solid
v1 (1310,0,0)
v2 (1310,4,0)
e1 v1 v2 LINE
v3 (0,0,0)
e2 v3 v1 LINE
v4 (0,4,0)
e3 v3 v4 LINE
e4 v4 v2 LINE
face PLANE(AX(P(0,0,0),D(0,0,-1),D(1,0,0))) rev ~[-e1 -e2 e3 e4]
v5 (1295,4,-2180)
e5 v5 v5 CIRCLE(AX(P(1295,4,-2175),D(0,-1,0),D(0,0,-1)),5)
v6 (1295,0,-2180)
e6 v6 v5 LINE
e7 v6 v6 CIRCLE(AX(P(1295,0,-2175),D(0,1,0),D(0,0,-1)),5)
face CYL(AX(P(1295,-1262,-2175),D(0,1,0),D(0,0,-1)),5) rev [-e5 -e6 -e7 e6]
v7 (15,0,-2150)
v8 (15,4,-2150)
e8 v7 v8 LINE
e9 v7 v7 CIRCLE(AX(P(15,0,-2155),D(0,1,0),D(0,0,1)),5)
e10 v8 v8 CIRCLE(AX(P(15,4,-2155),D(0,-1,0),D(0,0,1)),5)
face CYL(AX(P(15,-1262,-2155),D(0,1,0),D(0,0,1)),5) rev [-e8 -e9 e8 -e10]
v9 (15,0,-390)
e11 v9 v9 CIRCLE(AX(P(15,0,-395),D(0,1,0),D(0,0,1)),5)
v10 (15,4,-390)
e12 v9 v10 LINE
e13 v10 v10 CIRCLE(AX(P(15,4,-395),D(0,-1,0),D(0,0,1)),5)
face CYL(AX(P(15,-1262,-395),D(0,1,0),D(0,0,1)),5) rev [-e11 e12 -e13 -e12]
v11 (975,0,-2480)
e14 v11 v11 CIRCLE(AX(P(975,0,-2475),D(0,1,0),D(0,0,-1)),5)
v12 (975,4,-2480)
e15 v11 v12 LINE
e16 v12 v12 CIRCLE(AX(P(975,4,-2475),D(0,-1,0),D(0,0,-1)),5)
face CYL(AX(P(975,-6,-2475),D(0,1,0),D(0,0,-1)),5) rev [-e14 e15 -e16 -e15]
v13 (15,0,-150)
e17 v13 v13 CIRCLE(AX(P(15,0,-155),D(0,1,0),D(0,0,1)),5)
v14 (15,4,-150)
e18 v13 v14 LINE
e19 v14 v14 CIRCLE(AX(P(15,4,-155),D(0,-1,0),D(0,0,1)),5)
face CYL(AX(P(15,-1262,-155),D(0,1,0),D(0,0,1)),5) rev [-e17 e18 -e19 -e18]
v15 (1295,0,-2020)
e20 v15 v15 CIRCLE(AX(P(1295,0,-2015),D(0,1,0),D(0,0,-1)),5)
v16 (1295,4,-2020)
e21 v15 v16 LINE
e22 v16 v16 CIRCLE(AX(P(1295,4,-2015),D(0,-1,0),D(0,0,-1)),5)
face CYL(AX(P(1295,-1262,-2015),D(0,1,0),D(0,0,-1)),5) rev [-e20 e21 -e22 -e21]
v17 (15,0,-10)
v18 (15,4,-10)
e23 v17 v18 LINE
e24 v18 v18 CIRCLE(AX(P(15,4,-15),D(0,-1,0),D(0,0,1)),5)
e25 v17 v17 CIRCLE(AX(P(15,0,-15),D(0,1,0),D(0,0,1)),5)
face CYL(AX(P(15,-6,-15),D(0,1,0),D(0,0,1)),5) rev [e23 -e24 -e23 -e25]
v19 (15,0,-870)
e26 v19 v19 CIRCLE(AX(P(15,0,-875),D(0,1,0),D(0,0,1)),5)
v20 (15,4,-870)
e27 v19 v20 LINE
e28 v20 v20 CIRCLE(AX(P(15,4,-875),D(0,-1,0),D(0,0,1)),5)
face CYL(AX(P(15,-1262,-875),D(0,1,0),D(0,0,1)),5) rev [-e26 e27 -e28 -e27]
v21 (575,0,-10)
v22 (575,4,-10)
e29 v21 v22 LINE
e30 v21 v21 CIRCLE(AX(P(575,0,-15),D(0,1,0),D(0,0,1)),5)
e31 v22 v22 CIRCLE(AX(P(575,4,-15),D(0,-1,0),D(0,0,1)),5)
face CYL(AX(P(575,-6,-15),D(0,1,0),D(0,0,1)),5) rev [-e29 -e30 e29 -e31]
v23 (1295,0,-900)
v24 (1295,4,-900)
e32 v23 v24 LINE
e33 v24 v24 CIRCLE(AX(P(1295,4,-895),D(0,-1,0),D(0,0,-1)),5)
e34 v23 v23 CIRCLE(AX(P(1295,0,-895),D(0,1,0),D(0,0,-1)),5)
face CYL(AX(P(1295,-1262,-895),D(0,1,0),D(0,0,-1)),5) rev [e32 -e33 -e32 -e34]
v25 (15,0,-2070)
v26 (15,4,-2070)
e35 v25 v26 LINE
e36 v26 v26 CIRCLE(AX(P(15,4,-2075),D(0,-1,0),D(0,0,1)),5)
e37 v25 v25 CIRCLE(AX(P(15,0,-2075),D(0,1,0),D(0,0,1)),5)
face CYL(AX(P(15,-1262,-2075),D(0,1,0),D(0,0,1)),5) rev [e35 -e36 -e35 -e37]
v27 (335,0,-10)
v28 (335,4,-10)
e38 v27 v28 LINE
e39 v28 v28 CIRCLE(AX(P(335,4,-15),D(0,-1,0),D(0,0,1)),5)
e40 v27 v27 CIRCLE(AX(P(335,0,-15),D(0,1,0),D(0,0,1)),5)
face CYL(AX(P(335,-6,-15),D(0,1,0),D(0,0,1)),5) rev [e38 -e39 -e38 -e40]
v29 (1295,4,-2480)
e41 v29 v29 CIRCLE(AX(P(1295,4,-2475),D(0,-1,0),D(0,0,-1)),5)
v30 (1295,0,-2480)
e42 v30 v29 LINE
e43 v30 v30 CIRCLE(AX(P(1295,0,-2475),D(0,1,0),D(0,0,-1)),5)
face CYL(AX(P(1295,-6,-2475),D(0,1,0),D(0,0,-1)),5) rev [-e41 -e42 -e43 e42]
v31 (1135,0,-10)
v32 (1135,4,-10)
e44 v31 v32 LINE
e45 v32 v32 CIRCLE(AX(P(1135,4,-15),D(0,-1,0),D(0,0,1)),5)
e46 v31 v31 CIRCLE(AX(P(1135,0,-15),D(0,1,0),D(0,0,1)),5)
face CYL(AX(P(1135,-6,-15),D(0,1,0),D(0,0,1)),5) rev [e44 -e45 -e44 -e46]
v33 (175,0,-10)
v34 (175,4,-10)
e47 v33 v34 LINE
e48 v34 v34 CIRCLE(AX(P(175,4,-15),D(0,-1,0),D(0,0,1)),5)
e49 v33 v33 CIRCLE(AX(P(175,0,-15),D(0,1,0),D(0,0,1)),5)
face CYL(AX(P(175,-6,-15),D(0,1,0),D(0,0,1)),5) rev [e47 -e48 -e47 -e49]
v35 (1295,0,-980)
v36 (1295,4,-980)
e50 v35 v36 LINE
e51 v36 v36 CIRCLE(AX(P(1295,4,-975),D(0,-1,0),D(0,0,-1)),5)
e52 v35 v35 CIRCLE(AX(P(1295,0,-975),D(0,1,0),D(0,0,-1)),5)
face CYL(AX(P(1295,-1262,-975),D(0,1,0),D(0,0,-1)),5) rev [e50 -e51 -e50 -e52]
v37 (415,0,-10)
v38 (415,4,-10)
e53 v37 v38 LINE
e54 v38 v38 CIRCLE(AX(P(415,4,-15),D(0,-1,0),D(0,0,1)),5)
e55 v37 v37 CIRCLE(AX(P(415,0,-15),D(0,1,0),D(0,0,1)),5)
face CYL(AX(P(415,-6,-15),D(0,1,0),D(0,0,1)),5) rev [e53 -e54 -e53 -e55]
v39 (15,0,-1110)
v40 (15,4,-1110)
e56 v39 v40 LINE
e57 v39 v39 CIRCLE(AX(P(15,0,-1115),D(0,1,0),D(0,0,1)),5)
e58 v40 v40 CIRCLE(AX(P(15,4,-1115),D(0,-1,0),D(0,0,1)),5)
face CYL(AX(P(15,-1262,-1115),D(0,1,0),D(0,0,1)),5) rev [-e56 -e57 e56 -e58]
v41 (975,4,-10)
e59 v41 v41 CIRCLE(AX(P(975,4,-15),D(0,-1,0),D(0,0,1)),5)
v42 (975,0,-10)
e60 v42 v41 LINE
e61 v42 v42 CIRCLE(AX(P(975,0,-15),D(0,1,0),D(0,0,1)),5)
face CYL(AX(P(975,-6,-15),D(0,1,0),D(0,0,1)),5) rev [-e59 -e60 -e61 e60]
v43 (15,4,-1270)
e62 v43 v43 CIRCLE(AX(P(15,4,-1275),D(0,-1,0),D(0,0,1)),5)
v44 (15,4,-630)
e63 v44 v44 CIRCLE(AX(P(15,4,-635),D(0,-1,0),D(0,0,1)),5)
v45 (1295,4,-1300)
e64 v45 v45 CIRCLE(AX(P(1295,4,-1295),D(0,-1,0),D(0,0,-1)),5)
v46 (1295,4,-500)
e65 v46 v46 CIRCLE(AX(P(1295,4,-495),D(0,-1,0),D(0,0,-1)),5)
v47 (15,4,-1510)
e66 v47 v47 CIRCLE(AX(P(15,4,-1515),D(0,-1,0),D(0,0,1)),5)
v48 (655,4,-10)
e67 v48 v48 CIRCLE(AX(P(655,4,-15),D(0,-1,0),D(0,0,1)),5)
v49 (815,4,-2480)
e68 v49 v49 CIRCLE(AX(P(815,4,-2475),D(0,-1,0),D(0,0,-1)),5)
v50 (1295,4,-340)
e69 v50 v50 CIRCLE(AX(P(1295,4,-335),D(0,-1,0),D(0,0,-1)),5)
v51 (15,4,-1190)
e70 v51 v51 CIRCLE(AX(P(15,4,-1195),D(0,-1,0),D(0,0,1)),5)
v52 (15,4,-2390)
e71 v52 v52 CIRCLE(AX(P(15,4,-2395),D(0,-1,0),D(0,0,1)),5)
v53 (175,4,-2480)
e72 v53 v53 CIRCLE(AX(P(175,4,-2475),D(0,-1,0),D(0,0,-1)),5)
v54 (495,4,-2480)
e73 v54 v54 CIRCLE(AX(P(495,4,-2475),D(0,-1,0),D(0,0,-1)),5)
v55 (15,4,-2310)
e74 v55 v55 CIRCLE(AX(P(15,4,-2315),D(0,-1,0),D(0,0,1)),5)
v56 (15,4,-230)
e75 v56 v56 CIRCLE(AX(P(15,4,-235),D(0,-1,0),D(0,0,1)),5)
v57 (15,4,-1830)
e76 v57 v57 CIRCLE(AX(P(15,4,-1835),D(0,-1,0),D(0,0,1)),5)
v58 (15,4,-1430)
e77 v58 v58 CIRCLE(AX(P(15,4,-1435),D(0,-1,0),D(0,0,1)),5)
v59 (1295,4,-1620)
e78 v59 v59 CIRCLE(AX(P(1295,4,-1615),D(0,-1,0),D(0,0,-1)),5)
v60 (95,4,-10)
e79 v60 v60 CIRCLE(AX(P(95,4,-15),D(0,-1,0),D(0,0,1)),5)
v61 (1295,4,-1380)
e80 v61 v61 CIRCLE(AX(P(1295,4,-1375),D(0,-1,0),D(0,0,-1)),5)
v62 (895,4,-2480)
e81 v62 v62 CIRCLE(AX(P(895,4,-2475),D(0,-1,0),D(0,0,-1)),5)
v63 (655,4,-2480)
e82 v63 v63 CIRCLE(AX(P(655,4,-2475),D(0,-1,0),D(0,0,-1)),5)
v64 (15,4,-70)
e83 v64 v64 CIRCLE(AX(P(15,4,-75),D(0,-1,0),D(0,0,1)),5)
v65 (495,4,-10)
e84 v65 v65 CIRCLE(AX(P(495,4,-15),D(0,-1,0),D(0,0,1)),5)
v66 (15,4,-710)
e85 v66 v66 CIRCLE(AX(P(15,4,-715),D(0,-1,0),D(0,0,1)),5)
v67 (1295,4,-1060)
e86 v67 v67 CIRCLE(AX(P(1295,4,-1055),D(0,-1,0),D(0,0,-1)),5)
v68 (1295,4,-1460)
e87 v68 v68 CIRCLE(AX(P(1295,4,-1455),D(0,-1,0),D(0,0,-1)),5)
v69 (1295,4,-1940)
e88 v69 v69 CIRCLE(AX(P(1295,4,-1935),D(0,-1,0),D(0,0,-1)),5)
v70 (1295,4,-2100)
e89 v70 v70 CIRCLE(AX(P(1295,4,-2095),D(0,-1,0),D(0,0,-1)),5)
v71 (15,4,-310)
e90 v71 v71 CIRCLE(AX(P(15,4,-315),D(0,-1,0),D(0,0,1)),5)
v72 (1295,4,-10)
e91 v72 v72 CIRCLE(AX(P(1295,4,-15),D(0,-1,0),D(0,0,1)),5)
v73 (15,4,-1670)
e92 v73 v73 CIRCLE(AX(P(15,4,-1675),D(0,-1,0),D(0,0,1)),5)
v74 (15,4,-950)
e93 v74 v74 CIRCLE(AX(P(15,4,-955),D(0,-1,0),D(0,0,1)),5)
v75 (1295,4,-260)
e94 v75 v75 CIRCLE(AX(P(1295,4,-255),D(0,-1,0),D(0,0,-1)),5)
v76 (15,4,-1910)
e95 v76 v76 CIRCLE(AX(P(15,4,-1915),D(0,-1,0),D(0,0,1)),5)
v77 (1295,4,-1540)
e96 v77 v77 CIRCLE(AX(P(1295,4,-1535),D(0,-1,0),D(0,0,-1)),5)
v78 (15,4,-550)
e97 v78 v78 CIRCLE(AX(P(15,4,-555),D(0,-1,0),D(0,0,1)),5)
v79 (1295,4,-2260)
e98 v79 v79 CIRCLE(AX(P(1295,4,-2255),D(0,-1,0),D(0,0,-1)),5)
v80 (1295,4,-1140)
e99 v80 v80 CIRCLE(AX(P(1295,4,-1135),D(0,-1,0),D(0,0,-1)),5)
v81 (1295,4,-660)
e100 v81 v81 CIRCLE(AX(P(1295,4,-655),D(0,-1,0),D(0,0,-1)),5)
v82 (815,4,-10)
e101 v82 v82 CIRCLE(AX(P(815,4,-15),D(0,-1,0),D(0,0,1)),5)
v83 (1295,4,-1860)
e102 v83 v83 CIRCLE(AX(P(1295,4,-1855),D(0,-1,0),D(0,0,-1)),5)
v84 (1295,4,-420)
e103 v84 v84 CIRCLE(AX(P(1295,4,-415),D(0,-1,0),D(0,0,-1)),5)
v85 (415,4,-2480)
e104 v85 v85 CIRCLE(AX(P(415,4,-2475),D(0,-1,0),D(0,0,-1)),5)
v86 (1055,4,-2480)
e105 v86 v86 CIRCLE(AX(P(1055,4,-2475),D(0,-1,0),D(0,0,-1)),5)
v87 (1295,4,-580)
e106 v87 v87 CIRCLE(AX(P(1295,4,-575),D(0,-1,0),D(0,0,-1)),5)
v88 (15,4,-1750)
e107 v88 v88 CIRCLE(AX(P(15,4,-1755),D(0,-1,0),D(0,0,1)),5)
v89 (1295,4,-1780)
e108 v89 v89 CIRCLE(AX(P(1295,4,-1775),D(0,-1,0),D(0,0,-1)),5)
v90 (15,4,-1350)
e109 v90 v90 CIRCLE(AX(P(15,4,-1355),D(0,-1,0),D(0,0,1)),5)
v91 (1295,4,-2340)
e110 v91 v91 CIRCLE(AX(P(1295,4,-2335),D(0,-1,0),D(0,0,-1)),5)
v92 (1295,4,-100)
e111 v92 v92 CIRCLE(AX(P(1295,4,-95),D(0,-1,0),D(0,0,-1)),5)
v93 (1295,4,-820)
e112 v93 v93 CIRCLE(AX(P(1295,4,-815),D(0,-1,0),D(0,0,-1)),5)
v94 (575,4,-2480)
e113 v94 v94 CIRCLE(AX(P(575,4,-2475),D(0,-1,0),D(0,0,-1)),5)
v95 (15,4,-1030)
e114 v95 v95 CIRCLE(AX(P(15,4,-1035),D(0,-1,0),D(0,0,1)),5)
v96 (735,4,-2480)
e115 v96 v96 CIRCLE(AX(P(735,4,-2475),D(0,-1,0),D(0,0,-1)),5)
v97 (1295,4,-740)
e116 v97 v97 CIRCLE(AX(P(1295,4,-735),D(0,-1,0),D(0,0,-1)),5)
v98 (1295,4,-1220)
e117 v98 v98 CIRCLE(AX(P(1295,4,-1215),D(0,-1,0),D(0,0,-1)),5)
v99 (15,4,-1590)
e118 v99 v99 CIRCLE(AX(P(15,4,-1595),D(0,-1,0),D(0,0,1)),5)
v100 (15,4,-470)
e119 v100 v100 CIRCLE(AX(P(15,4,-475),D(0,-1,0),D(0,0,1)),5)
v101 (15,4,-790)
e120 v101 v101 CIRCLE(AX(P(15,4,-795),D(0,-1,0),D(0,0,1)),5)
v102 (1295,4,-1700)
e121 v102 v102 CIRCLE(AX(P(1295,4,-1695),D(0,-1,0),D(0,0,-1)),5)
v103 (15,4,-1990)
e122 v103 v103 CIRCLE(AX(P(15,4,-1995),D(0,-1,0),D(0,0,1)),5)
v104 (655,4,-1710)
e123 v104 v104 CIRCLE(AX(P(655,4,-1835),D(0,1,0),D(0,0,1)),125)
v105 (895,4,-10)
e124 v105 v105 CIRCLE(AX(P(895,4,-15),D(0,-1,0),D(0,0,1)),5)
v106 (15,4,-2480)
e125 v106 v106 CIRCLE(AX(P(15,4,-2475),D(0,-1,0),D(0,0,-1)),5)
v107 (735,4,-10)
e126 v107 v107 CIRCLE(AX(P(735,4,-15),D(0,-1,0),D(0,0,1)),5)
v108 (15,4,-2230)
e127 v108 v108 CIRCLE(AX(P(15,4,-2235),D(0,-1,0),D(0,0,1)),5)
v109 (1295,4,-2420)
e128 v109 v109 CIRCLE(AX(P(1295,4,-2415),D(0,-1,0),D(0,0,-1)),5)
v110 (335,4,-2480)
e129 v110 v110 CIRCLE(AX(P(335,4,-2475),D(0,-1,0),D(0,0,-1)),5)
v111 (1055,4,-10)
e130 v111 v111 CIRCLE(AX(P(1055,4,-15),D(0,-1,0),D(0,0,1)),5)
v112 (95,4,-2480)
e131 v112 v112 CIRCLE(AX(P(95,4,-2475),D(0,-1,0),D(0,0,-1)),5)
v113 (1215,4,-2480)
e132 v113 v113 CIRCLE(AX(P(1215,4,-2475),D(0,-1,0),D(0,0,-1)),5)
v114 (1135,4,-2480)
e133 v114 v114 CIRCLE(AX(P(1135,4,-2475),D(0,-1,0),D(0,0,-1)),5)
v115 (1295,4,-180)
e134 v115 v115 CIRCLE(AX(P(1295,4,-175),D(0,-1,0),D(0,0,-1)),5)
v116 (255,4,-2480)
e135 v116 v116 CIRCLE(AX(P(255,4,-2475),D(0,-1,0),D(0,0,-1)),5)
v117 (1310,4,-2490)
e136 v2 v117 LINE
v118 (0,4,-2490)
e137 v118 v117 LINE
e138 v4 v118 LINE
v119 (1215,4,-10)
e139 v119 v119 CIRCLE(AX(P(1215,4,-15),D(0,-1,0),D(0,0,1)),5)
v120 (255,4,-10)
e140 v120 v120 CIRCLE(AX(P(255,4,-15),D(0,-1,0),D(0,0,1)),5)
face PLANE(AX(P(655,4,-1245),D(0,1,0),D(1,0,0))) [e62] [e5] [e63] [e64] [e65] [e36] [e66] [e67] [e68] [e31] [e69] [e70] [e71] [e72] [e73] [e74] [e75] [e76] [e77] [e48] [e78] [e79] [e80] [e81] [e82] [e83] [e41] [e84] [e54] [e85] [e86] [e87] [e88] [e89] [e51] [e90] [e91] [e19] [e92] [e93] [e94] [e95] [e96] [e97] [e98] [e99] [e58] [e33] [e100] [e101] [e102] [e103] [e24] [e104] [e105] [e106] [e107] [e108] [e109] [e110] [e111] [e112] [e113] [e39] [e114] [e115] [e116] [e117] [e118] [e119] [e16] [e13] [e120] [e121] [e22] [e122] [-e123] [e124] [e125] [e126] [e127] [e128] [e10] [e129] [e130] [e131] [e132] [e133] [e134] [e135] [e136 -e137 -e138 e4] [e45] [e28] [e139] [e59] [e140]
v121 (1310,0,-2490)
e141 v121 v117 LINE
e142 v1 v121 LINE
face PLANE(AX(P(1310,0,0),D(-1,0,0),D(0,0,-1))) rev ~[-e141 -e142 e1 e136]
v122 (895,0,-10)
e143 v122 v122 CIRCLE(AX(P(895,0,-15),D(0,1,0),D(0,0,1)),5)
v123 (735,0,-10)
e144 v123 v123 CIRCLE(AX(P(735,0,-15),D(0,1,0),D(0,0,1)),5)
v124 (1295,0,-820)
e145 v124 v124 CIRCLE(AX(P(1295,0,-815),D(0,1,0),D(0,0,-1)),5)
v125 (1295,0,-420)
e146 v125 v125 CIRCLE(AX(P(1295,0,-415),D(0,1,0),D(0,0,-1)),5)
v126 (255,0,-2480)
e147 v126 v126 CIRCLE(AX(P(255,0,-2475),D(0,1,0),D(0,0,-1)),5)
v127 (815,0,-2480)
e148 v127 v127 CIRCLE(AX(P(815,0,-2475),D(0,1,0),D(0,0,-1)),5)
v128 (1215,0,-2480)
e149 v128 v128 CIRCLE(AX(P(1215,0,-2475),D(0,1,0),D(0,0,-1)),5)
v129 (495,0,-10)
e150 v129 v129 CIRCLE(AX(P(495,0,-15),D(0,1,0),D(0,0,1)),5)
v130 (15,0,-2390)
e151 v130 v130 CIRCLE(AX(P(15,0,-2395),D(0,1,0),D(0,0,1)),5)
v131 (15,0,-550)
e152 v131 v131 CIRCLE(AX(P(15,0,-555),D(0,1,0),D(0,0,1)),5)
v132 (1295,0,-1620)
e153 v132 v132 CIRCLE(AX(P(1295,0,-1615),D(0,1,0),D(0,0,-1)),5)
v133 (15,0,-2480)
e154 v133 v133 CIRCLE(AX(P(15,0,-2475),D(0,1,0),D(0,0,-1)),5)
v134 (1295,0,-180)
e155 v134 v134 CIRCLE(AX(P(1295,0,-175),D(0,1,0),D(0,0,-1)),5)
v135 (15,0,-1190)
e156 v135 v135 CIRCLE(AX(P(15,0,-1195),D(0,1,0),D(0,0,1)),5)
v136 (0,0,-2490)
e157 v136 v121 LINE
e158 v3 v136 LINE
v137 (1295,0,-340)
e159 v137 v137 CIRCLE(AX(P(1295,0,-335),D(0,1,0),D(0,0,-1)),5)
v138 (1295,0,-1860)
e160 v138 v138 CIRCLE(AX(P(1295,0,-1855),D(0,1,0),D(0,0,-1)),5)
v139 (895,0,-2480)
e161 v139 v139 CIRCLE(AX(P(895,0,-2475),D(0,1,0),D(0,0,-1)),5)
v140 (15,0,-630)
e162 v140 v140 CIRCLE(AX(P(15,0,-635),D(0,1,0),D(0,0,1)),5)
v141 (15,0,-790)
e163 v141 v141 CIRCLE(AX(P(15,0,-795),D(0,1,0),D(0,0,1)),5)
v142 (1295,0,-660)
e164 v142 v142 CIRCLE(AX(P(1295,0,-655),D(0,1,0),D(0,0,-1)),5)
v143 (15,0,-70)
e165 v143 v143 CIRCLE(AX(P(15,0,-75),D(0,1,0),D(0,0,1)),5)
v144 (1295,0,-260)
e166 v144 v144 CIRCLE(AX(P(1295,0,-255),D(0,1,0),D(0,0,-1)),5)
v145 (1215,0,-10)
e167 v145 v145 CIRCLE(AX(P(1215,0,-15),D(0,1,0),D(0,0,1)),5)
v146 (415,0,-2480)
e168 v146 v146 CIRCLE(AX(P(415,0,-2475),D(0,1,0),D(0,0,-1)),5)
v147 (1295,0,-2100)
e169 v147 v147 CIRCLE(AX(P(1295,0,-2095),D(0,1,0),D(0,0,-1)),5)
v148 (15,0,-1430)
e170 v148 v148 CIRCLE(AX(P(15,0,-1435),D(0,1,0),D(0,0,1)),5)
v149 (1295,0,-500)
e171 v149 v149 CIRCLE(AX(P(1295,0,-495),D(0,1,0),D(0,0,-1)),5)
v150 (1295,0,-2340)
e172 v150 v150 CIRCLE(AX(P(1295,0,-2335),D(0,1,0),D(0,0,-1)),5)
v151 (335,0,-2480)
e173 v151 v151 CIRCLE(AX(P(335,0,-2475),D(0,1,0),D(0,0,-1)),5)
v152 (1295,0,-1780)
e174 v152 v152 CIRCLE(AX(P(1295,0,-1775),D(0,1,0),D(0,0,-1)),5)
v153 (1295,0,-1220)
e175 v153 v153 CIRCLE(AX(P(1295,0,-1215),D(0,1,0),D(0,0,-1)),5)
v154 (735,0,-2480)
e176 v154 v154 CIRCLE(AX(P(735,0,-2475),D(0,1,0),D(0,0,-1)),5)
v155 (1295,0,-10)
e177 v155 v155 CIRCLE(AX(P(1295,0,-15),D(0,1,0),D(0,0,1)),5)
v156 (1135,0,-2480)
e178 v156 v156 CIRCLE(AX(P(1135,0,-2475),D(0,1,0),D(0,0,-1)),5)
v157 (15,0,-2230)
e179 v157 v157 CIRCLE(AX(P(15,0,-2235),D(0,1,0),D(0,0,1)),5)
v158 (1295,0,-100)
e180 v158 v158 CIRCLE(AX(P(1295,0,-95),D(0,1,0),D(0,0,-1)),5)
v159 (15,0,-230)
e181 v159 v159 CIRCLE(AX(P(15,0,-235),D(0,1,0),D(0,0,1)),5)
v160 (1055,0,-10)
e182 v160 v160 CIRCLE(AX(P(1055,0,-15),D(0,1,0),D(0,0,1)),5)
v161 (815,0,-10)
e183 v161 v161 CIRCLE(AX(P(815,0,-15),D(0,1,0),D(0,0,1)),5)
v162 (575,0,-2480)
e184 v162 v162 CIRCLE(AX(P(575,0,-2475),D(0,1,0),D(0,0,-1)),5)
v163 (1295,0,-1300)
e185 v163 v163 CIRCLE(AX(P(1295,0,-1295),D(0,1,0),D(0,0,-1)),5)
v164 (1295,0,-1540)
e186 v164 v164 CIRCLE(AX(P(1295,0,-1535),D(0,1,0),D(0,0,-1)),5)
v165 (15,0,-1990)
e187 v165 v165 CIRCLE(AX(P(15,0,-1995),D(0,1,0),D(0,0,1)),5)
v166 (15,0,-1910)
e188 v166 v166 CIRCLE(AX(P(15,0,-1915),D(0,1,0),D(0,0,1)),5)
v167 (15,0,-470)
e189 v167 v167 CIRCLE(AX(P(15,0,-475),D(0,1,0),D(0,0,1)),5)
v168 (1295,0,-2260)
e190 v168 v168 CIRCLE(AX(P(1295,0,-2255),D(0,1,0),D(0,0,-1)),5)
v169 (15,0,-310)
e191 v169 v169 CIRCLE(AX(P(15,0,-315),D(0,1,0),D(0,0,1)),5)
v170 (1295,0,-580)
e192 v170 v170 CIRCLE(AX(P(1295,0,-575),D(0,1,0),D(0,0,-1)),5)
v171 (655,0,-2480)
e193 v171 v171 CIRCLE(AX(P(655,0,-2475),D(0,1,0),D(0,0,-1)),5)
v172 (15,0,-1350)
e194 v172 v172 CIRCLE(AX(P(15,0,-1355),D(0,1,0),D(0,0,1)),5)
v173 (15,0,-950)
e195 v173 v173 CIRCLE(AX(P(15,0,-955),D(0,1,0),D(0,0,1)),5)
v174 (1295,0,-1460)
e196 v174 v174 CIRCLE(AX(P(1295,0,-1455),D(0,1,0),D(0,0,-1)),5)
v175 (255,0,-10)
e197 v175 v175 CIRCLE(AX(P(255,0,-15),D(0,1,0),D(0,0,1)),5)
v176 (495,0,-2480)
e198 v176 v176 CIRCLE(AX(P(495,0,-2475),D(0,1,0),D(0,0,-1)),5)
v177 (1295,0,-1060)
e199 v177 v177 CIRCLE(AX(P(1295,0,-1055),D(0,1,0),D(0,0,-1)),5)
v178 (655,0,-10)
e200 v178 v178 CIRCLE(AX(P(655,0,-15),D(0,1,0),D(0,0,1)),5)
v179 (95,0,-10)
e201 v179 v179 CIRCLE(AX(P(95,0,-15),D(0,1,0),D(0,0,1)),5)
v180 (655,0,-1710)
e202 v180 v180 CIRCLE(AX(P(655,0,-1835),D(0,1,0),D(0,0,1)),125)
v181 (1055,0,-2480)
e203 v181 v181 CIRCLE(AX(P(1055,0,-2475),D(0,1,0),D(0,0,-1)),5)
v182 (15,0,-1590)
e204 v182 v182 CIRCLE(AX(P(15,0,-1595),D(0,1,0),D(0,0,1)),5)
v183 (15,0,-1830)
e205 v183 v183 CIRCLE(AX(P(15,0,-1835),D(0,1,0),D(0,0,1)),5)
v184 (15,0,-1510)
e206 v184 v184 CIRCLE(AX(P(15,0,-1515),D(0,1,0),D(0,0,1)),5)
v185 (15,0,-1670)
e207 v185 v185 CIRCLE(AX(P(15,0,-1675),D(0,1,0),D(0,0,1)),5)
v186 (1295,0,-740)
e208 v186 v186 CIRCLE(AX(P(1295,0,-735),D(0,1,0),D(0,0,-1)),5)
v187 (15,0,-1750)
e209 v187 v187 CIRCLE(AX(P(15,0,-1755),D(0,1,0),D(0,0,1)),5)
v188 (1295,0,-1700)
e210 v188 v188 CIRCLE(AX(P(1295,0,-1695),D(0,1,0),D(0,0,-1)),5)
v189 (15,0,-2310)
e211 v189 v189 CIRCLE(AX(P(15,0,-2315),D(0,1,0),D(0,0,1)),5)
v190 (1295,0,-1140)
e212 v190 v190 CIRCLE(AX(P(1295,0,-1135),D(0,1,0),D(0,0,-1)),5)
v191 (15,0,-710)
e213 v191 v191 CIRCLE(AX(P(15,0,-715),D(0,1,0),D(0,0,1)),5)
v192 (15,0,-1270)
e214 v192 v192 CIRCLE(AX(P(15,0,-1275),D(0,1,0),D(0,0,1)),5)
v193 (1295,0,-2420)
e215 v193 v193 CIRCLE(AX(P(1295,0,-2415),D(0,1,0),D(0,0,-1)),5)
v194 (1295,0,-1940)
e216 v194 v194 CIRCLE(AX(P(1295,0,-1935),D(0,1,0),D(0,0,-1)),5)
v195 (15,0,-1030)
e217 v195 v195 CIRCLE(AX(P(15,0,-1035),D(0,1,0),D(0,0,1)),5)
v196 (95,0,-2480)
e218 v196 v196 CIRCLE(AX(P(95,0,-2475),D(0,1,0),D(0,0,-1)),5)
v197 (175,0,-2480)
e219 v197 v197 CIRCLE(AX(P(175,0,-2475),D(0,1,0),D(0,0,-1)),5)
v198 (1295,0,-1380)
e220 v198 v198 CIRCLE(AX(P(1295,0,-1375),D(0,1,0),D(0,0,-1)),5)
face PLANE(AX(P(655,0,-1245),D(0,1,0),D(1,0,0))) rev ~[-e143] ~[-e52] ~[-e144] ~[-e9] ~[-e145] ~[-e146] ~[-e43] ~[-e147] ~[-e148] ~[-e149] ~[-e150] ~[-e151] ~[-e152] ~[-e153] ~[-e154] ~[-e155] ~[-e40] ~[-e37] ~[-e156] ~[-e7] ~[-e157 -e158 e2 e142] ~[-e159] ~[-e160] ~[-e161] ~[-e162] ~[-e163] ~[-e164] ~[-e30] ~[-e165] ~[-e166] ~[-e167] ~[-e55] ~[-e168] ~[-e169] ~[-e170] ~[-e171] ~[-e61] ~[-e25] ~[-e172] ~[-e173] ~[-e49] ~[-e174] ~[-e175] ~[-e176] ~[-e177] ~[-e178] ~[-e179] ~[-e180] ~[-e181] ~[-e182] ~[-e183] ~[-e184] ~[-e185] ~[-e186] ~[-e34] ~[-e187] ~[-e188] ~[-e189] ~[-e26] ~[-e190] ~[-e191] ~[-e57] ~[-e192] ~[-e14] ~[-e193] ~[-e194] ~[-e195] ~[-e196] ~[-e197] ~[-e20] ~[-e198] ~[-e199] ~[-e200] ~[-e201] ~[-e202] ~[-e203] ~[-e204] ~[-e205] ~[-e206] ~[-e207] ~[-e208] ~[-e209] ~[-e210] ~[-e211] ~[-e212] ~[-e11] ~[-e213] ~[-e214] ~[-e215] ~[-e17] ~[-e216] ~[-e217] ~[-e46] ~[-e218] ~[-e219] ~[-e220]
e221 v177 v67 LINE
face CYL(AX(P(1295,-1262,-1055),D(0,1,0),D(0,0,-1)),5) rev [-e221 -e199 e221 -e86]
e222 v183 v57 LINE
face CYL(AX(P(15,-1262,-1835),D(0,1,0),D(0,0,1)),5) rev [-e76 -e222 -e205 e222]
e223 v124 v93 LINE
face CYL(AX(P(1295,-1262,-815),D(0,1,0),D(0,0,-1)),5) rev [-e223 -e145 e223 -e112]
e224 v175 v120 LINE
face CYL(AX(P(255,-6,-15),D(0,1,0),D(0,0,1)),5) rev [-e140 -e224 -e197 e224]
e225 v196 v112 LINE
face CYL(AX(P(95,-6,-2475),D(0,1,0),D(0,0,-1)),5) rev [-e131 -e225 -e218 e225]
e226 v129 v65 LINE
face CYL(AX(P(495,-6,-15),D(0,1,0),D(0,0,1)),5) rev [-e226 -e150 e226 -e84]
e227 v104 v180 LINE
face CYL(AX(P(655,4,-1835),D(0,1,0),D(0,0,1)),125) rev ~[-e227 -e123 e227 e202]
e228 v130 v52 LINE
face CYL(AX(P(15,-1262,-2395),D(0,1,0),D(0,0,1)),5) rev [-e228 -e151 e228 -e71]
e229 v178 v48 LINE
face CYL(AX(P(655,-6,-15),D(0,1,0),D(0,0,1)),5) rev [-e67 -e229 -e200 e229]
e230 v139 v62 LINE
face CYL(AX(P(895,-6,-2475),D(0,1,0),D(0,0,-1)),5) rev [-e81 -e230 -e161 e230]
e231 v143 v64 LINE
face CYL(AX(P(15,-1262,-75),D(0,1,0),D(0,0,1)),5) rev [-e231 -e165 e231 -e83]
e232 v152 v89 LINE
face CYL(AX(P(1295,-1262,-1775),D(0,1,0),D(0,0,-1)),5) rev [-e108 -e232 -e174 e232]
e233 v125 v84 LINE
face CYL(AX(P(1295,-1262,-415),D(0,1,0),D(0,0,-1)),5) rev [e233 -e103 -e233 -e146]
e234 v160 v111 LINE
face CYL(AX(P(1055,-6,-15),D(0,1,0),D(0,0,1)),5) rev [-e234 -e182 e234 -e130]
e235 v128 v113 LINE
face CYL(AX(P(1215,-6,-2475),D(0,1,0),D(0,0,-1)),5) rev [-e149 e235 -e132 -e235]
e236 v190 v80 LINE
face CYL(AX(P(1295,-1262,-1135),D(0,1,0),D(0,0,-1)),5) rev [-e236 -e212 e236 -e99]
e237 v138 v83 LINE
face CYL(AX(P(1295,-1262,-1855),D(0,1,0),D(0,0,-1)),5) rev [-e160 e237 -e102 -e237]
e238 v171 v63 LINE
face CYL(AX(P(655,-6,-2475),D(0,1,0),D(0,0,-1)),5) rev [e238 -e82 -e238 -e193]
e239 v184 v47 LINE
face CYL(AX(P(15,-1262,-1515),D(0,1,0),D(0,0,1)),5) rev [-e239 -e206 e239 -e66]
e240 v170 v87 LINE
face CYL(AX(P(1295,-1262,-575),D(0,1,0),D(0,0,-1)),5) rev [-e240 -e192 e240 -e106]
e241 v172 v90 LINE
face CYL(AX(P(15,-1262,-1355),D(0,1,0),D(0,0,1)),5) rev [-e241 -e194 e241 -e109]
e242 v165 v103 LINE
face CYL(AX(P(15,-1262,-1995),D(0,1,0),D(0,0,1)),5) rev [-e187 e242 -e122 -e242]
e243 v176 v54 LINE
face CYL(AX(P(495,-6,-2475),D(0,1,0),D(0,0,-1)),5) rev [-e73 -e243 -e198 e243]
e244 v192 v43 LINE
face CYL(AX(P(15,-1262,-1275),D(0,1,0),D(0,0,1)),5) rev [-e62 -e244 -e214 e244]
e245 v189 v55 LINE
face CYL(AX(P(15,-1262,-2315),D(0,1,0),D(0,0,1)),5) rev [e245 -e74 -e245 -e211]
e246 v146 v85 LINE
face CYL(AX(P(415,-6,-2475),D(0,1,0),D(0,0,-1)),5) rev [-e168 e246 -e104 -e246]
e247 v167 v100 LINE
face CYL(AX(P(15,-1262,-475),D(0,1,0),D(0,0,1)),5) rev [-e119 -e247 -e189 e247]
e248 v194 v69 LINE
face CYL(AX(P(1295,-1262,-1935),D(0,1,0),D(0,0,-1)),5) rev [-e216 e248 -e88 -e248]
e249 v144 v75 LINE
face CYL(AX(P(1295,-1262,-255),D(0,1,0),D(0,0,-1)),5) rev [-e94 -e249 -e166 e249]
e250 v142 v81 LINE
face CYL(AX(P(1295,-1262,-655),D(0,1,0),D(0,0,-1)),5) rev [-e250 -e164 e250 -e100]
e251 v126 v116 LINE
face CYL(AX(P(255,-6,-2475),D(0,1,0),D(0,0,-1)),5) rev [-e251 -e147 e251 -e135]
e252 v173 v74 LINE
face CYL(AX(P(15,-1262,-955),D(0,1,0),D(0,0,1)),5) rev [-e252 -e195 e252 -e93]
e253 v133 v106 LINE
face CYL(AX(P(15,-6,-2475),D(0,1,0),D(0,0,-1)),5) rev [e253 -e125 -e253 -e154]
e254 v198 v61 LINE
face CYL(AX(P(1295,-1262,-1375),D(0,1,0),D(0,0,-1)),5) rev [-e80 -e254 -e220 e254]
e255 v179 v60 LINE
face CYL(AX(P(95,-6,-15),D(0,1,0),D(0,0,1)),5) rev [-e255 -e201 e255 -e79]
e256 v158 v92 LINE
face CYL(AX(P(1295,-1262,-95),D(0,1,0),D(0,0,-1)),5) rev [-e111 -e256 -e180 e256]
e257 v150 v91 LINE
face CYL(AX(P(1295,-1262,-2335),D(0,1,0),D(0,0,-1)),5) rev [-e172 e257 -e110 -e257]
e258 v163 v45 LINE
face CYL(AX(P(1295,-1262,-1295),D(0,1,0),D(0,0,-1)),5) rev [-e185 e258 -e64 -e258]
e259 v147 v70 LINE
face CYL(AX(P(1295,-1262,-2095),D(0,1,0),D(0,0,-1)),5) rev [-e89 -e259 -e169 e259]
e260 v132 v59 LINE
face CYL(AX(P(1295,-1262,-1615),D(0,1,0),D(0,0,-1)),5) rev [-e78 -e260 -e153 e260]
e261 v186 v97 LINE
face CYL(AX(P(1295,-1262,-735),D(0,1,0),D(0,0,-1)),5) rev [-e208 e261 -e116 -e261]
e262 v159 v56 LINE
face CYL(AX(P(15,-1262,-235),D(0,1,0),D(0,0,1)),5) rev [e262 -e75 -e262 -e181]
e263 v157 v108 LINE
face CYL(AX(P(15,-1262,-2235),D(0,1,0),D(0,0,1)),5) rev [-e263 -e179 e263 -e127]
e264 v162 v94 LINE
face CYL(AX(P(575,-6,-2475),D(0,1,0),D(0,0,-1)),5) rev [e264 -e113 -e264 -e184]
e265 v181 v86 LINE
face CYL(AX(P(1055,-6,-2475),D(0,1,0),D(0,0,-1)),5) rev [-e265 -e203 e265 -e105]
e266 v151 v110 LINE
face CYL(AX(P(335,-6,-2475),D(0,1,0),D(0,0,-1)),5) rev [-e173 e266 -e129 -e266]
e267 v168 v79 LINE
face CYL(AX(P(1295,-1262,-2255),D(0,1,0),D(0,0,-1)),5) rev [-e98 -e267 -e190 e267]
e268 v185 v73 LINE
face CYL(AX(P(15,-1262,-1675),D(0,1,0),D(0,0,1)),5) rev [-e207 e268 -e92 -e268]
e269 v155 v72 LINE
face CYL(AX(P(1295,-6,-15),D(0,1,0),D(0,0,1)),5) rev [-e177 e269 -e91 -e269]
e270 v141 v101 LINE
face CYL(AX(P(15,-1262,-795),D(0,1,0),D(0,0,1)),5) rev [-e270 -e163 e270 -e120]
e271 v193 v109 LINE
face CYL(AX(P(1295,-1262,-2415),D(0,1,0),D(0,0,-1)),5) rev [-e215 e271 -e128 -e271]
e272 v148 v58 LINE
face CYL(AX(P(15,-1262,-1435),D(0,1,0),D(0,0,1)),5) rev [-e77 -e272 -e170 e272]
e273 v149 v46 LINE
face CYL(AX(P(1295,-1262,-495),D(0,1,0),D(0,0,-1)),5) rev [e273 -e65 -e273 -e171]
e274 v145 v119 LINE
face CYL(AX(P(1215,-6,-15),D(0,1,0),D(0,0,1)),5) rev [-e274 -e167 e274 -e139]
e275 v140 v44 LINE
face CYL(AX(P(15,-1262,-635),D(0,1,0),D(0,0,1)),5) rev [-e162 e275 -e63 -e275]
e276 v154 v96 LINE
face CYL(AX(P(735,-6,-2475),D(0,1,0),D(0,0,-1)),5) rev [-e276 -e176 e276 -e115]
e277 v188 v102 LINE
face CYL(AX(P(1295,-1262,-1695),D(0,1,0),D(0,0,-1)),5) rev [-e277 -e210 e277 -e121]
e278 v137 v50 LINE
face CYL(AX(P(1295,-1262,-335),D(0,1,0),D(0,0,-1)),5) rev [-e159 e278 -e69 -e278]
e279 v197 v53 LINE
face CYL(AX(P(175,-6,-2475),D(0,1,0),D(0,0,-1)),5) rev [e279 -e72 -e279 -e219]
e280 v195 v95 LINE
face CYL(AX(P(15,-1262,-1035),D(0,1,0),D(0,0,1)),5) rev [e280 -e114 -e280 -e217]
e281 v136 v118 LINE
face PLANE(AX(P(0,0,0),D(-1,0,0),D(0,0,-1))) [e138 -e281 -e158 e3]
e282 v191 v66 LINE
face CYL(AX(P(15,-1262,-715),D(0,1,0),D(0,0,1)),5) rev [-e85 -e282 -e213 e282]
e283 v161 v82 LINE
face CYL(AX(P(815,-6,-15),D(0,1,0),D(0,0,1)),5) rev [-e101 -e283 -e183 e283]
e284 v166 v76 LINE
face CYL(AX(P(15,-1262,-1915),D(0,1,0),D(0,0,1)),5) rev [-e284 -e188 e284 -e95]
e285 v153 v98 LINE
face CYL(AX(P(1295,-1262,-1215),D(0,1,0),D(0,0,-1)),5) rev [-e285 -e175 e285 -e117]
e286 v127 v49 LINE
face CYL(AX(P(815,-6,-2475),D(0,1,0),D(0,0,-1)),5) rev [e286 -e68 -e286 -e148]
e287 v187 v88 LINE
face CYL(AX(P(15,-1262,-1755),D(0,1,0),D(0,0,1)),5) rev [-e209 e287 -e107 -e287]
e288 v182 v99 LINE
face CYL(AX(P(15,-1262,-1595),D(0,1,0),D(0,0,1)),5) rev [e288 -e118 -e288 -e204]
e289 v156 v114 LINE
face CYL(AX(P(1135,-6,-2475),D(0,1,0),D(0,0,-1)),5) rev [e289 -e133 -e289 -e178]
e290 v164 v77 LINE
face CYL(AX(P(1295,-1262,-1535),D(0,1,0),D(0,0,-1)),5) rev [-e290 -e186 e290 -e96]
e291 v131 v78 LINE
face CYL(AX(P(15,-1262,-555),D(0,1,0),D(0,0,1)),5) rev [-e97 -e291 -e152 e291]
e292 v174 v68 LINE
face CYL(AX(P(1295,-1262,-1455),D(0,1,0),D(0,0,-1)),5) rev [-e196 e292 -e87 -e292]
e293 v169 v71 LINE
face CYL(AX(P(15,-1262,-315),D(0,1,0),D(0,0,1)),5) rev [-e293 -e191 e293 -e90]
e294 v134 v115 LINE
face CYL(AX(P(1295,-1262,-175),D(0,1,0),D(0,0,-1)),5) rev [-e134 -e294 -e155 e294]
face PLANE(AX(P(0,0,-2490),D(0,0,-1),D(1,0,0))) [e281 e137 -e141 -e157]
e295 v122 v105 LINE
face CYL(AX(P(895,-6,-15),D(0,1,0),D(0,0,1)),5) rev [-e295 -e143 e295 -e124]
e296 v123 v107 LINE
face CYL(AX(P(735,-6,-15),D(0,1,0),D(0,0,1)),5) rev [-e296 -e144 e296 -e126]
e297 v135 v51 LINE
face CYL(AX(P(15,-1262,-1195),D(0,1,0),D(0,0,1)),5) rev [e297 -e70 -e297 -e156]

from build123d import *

# Parameters (mm, degrees)
SKETCH_1_W               = 1310
SKETCH_1_H               = 2490
EXTRUDE_1_DEPTH          = 4
PATTERN_LINEAR_1_COUNT   = 17
PATTERN_LINEAR_1_PITCH   = 80
PATTERN_CIRCULAR_1_COUNT = 2
SKETCH_4_R               = 125
CUT_EXTRUDE_1_DEPTH      = 2814.577082648
PATTERN_LINEAR_2_COUNT   = 30
PATTERN_LINEAR_2_PITCH   = 80
PATTERN_CIRCULAR_2_COUNT = 2


with BuildPart() as part:
    # 草图1 → 凸台-拉伸1 (new body)
    with BuildSketch(Plane(origin=(0, 0, 0), x_dir=(1, 0, 0), z_dir=(0, 1, 0))):
        with Locations((655, 1245)):
            Rectangle(SKETCH_1_W, SKETCH_1_H)
    extrude(amount=EXTRUDE_1_DEPTH)

    # 草图2 → Ø10.0 (10) 直径孔1 (revolve, cut)
    with BuildSketch(Plane(origin=(15, 4, -15), x_dir=(0, 0, 1), z_dir=(1, 0, 0))):
        Polygon((0, 0), (0, 13.004303095), (5, 10), (5, 0), align=None)
    hole_wizard_10_0_10_1 = revolve(axis=Axis((15, 10.35, -15), (0, -1, 0)), mode=Mode.SUBTRACT)

    # 阵列(线性)1: Ø10.0 (10) 直径孔1 ×17
    with Locations(*[(i * PATTERN_LINEAR_1_PITCH, 0, 0) for i in range(1, PATTERN_LINEAR_1_COUNT)]):
        add(hole_wizard_10_0_10_1, mode=Mode.SUBTRACT)

    # 阵列(圆周)1: Ø10.0 (10) 直径孔1 ×2 about axis
    pattern_circular_1_axis = Axis((655, 0, -1245), (0, 1, 0))
    for i in range(1, PATTERN_CIRCULAR_1_COUNT):
        add(hole_wizard_10_0_10_1.rotate(pattern_circular_1_axis, i * 360 / PATTERN_CIRCULAR_1_COUNT), mode=Mode.SUBTRACT)

    # 阵列(圆周)1 copy 1 sketch → 阵列(圆周)1 copy 1 (revolve, cut)
    with BuildSketch(Plane(origin=(1215, 4, -2475), x_dir=(0, 0, -1), z_dir=(-1, 0, 0))):
        Polygon((0, 0), (0, 13.004303095), (5, 10), (5, 0), align=None)
    revolve(axis=Axis((1215, 10.35, -2475), (0, -1, 0)), mode=Mode.SUBTRACT)

    # 阵列(圆周)1 copy 2 sketch → 阵列(圆周)1 copy 2 (revolve, cut)
    with BuildSketch(Plane(origin=(1135, 4, -2475), x_dir=(0, 0, -1), z_dir=(-1, 0, 0))):
        Polygon((0, 0), (0, 13.004303095), (5, 10), (5, 0), align=None)
    revolve(axis=Axis((1135, 10.35, -2475), (0, -1, 0)), mode=Mode.SUBTRACT)

    # 阵列(圆周)1 copy 3 sketch → 阵列(圆周)1 copy 3 (revolve, cut)
    with BuildSketch(Plane(origin=(1055, 4, -2475), x_dir=(0, 0, -1), z_dir=(-1, 0, 0))):
        Polygon((0, 0), (0, 13.004303095), (5, 10), (5, 0), align=None)
    revolve(axis=Axis((1055, 10.35, -2475), (0, -1, 0)), mode=Mode.SUBTRACT)

    # 阵列(圆周)1 copy 4 sketch → 阵列(圆周)1 copy 4 (revolve, cut)
    with BuildSketch(Plane(origin=(975, 4, -2475), x_dir=(0, 0, -1), z_dir=(-1, 0, 0))):
        Polygon((0, 0), (0, 13.004303095), (5, 10), (5, 0), align=None)
    revolve(axis=Axis((975, 10.35, -2475), (0, -1, 0)), mode=Mode.SUBTRACT)

    # 阵列(圆周)1 copy 5 sketch → 阵列(圆周)1 copy 5 (revolve, cut)
    with BuildSketch(Plane(origin=(895, 4, -2475), x_dir=(0, 0, -1), z_dir=(-1, 0, 0))):
        Polygon((0, 0), (0, 13.004303095), (5, 10), (5, 0), align=None)
    revolve(axis=Axis((895, 10.35, -2475), (0, -1, 0)), mode=Mode.SUBTRACT)

    # 阵列(圆周)1 copy 6 sketch → 阵列(圆周)1 copy 6 (revolve, cut)
    with BuildSketch(Plane(origin=(815, 4, -2475), x_dir=(0, 0, -1), z_dir=(-1, 0, 0))):
        Polygon((0, 0), (0, 13.004303095), (5, 10), (5, 0), align=None)
    revolve(axis=Axis((815, 10.35, -2475), (0, -1, 0)), mode=Mode.SUBTRACT)

    # 阵列(圆周)1 copy 7 sketch → 阵列(圆周)1 copy 7 (revolve, cut)
    with BuildSketch(Plane(origin=(735, 4, -2475), x_dir=(0, 0, -1), z_dir=(-1, 0, 0))):
        Polygon((0, 0), (0, 13.004303095), (5, 10), (5, 0), align=None)
    revolve(axis=Axis((735, 10.35, -2475), (0, -1, 0)), mode=Mode.SUBTRACT)

    # 阵列(圆周)1 copy 8 sketch → 阵列(圆周)1 copy 8 (revolve, cut)
    with BuildSketch(Plane(origin=(655, 4, -2475), x_dir=(0, 0, -1), z_dir=(-1, 0, 0))):
        Polygon((0, 0), (0, 13.004303095), (5, 10), (5, 0), align=None)
    revolve(axis=Axis((655, 10.35, -2475), (0, -1, 0)), mode=Mode.SUBTRACT)

    # 阵列(圆周)1 copy 9 sketch → 阵列(圆周)1 copy 9 (revolve, cut)
    with BuildSketch(Plane(origin=(575, 4, -2475), x_dir=(0, 0, -1), z_dir=(-1, 0, 0))):
        Polygon((0, 0), (0, 13.004303095), (5, 10), (5, 0), align=None)
    revolve(axis=Axis((575, 10.35, -2475), (0, -1, 0)), mode=Mode.SUBTRACT)

    # 阵列(圆周)1 copy 10 sketch → 阵列(圆周)1 copy 10 (revolve, cut)
    with BuildSketch(Plane(origin=(495, 4, -2475), x_dir=(0, 0, -1), z_dir=(-1, 0, 0))):
        Polygon((0, 0), (0, 13.004303095), (5, 10), (5, 0), align=None)
    revolve(axis=Axis((495, 10.35, -2475), (0, -1, 0)), mode=Mode.SUBTRACT)

    # 阵列(圆周)1 copy 11 sketch → 阵列(圆周)1 copy 11 (revolve, cut)
    with BuildSketch(Plane(origin=(415, 4, -2475), x_dir=(0, 0, -1), z_dir=(-1, 0, 0))):
        Polygon((0, 0), (0, 13.004303095), (5, 10), (5, 0), align=None)
    revolve(axis=Axis((415, 10.35, -2475), (0, -1, 0)), mode=Mode.SUBTRACT)

    # 阵列(圆周)1 copy 12 sketch → 阵列(圆周)1 copy 12 (revolve, cut)
    with BuildSketch(Plane(origin=(335, 4, -2475), x_dir=(0, 0, -1), z_dir=(-1, 0, 0))):
        Polygon((0, 0), (0, 13.004303095), (5, 10), (5, 0), align=None)
    revolve(axis=Axis((335, 10.35, -2475), (0, -1, 0)), mode=Mode.SUBTRACT)

    # 阵列(圆周)1 copy 13 sketch → 阵列(圆周)1 copy 13 (revolve, cut)
    with BuildSketch(Plane(origin=(255, 4, -2475), x_dir=(0, 0, -1), z_dir=(-1, 0, 0))):
        Polygon((0, 0), (0, 13.004303095), (5, 10), (5, 0), align=None)
    revolve(axis=Axis((255, 10.35, -2475), (0, -1, 0)), mode=Mode.SUBTRACT)

    # 阵列(圆周)1 copy 14 sketch → 阵列(圆周)1 copy 14 (revolve, cut)
    with BuildSketch(Plane(origin=(175, 4, -2475), x_dir=(0, 0, -1), z_dir=(-1, 0, 0))):
        Polygon((0, 0), (0, 13.004303095), (5, 10), (5, 0), align=None)
    revolve(axis=Axis((175, 10.35, -2475), (0, -1, 0)), mode=Mode.SUBTRACT)

    # 阵列(圆周)1 copy 15 sketch → 阵列(圆周)1 copy 15 (revolve, cut)
    with BuildSketch(Plane(origin=(95, 4, -2475), x_dir=(0, 0, -1), z_dir=(-1, 0, 0))):
        Polygon((0, 0), (0, 13.004303095), (5, 10), (5, 0), align=None)
    revolve(axis=Axis((95, 10.35, -2475), (0, -1, 0)), mode=Mode.SUBTRACT)

    # 阵列(圆周)1 copy 16 sketch → 阵列(圆周)1 copy 16 (revolve, cut)
    with BuildSketch(Plane(origin=(15, 4, -2475), x_dir=(0, 0, -1), z_dir=(-1, 0, 0))):
        Polygon((0, 0), (0, 13.004303095), (5, 10), (5, 0), align=None)
    revolve(axis=Axis((15, 10.35, -2475), (0, -1, 0)), mode=Mode.SUBTRACT)

    # 草图4 → 切除-拉伸1 (cut, through all)
    with BuildSketch(Plane(origin=(0, 4, 0), x_dir=(1, 0, 0), z_dir=(0, 1, 0))):
        with Locations(Location((655, 1835, 0), (0, 0, 270))):
            Circle(SKETCH_4_R)
    extrude(amount=-CUT_EXTRUDE_1_DEPTH, mode=Mode.SUBTRACT)

    # 草图5 → Ø10.0 (10) 直径孔2 (revolve, cut)
    with BuildSketch(Plane(origin=(15, 4, -2395), x_dir=(0, 0, 1), z_dir=(1, 0, 0))):
        Polygon((0, 0), (0, 1269.004303095), (5, 1266), (5, 0), align=None)
    hole_wizard_10_0_10_2 = revolve(axis=Axis((15, 10.35, -2395), (0, -1, 0)), mode=Mode.SUBTRACT)

    # 阵列(线性)2: Ø10.0 (10) 直径孔2 ×30
    with Locations(*[(0, 0, i * PATTERN_LINEAR_2_PITCH) for i in range(1, PATTERN_LINEAR_2_COUNT)]):
        add(hole_wizard_10_0_10_2, mode=Mode.SUBTRACT)

    # 阵列(圆周)2: Ø10.0 (10) 直径孔2 ×2 about axis
    pattern_circular_2_axis = Axis((655, 0, -1245), (0, 1, 0))
    for i in range(1, PATTERN_CIRCULAR_2_COUNT):
        add(hole_wizard_10_0_10_2.rotate(pattern_circular_2_axis, i * 360 / PATTERN_CIRCULAR_2_COUNT), mode=Mode.SUBTRACT)

    # 阵列(圆周)2 copy 1 sketch → 阵列(圆周)2 copy 1 (revolve, cut)
    with BuildSketch(Plane(origin=(1295, 4, -175), x_dir=(0, 0, -1), z_dir=(-1, 0, 0))):
        Polygon((0, 0), (0, 1269.004303095), (5, 1266), (5, 0), align=None)
    revolve(axis=Axis((1295, 10.35, -175), (0, -1, 0)), mode=Mode.SUBTRACT)

    # 阵列(圆周)2 copy 2 sketch → 阵列(圆周)2 copy 2 (revolve, cut)
    with BuildSketch(Plane(origin=(1295, 4, -255), x_dir=(0, 0, -1), z_dir=(-1, 0, 0))):
        Polygon((0, 0), (0, 1269.004303095), (5, 1266), (5, 0), align=None)
    revolve(axis=Axis((1295, 10.35, -255), (0, -1, 0)), mode=Mode.SUBTRACT)

    # 阵列(圆周)2 copy 3 sketch → 阵列(圆周)2 copy 3 (revolve, cut)
    with BuildSketch(Plane(origin=(1295, 4, -335), x_dir=(0, 0, -1), z_dir=(-1, 0, 0))):
        Polygon((0, 0), (0, 1269.004303095), (5, 1266), (5, 0), align=None)
    revolve(axis=Axis((1295, 10.35, -335), (0, -1, 0)), mode=Mode.SUBTRACT)

    # 阵列(圆周)2 copy 4 sketch → 阵列(圆周)2 copy 4 (revolve, cut)
    with BuildSketch(Plane(origin=(1295, 4, -415), x_dir=(0, 0, -1), z_dir=(-1, 0, 0))):
        Polygon((0, 0), (0, 1269.004303095), (5, 1266), (5, 0), align=None)
    revolve(axis=Axis((1295, 10.35, -415), (0, -1, 0)), mode=Mode.SUBTRACT)

    # 阵列(圆周)2 copy 5 sketch → 阵列(圆周)2 copy 5 (revolve, cut)
    with BuildSketch(Plane(origin=(1295, 4, -495), x_dir=(0, 0, -1), z_dir=(-1, 0, 0))):
        Polygon((0, 0), (0, 1269.004303095), (5, 1266), (5, 0), align=None)
    revolve(axis=Axis((1295, 10.35, -495), (0, -1, 0)), mode=Mode.SUBTRACT)

    # 阵列(圆周)2 copy 6 sketch → 阵列(圆周)2 copy 6 (revolve, cut)
    with BuildSketch(Plane(origin=(1295, 4, -575), x_dir=(0, 0, -1), z_dir=(-1, 0, 0))):
        Polygon((0, 0), (0, 1269.004303095), (5, 1266), (5, 0), align=None)
    revolve(axis=Axis((1295, 10.35, -575), (0, -1, 0)), mode=Mode.SUBTRACT)

    # 阵列(圆周)2 copy 7 sketch → 阵列(圆周)2 copy 7 (revolve, cut)
    with BuildSketch(Plane(origin=(1295, 4, -655), x_dir=(0, 0, -1), z_dir=(-1, 0, 0))):
        Polygon((0, 0), (0, 1269.004303095), (5, 1266), (5, 0), align=None)
    revolve(axis=Axis((1295, 10.35, -655), (0, -1, 0)), mode=Mode.SUBTRACT)

    # 阵列(圆周)2 copy 8 sketch → 阵列(圆周)2 copy 8 (revolve, cut)
    with BuildSketch(Plane(origin=(1295, 4, -735), x_dir=(0, 0, -1), z_dir=(-1, 0, 0))):
        Polygon((0, 0), (0, 1269.004303095), (5, 1266), (5, 0), align=None)
    revolve(axis=Axis((1295, 10.35, -735), (0, -1, 0)), mode=Mode.SUBTRACT)

    # 阵列(圆周)2 copy 9 sketch → 阵列(圆周)2 copy 9 (revolve, cut)
    with BuildSketch(Plane(origin=(1295, 4, -815), x_dir=(0, 0, -1), z_dir=(-1, 0, 0))):
        Polygon((0, 0), (0, 1269.004303095), (5, 1266), (5, 0), align=None)
    revolve(axis=Axis((1295, 10.35, -815), (0, -1, 0)), mode=Mode.SUBTRACT)

    # 阵列(圆周)2 copy 10 sketch → 阵列(圆周)2 copy 10 (revolve, cut)
    with BuildSketch(Plane(origin=(1295, 4, -895), x_dir=(0, 0, -1), z_dir=(-1, 0, 0))):
        Polygon((0, 0), (0, 1269.004303095), (5, 1266), (5, 0), align=None)
    revolve(axis=Axis((1295, 10.35, -895), (0, -1, 0)), mode=Mode.SUBTRACT)

    # 阵列(圆周)2 copy 11 sketch → 阵列(圆周)2 copy 11 (revolve, cut)
    with BuildSketch(Plane(origin=(1295, 4, -975), x_dir=(0, 0, -1), z_dir=(-1, 0, 0))):
        Polygon((0, 0), (0, 1269.004303095), (5, 1266), (5, 0), align=None)
    revolve(axis=Axis((1295, 10.35, -975), (0, -1, 0)), mode=Mode.SUBTRACT)

    # 阵列(圆周)2 copy 12 sketch → 阵列(圆周)2 copy 12 (revolve, cut)
    with BuildSketch(Plane(origin=(1295, 4, -1055), x_dir=(0, 0, -1), z_dir=(-1, 0, 0))):
        Polygon((0, 0), (0, 1269.004303095), (5, 1266), (5, 0), align=None)
    revolve(axis=Axis((1295, 10.35, -1055), (0, -1, 0)), mode=Mode.SUBTRACT)

    # 阵列(圆周)2 copy 13 sketch → 阵列(圆周)2 copy 13 (revolve, cut)
    with BuildSketch(Plane(origin=(1295, 4, -1135), x_dir=(0, 0, -1), z_dir=(-1, 0, 0))):
        Polygon((0, 0), (0, 1269.004303095), (5, 1266), (5, 0), align=None)
    revolve(axis=Axis((1295, 10.35, -1135), (0, -1, 0)), mode=Mode.SUBTRACT)

    # 阵列(圆周)2 copy 14 sketch → 阵列(圆周)2 copy 14 (revolve, cut)
    with BuildSketch(Plane(origin=(1295, 4, -1215), x_dir=(0, 0, -1), z_dir=(-1, 0, 0))):
        Polygon((0, 0), (0, 1269.004303095), (5, 1266), (5, 0), align=None)
    revolve(axis=Axis((1295, 10.35, -1215), (0, -1, 0)), mode=Mode.SUBTRACT)

    # 阵列(圆周)2 copy 15 sketch → 阵列(圆周)2 copy 15 (revolve, cut)
    with BuildSketch(Plane(origin=(1295, 4, -1295), x_dir=(0, 0, -1), z_dir=(-1, 0, 0))):
        Polygon((0, 0), (0, 1269.004303095), (5, 1266), (5, 0), align=None)
    revolve(axis=Axis((1295, 10.35, -1295), (0, -1, 0)), mode=Mode.SUBTRACT)

    # 阵列(圆周)2 copy 16 sketch → 阵列(圆周)2 copy 16 (revolve, cut)
    with BuildSketch(Plane(origin=(1295, 4, -1375), x_dir=(0, 0, -1), z_dir=(-1, 0, 0))):
        Polygon((0, 0), (0, 1269.004303095), (5, 1266), (5, 0), align=None)
    revolve(axis=Axis((1295, 10.35, -1375), (0, -1, 0)), mode=Mode.SUBTRACT)

    # 阵列(圆周)2 copy 17 sketch → 阵列(圆周)2 copy 17 (revolve, cut)
    with BuildSketch(Plane(origin=(1295, 4, -1455), x_dir=(0, 0, -1), z_dir=(-1, 0, 0))):
        Polygon((0, 0), (0, 1269.004303095), (5, 1266), (5, 0), align=None)
    revolve(axis=Axis((1295, 10.35, -1455), (0, -1, 0)), mode=Mode.SUBTRACT)

    # 阵列(圆周)2 copy 18 sketch → 阵列(圆周)2 copy 18 (revolve, cut)
    with BuildSketch(Plane(origin=(1295, 4, -1535), x_dir=(0, 0, -1), z_dir=(-1, 0, 0))):
        Polygon((0, 0), (0, 1269.004303095), (5, 1266), (5, 0), align=None)
    revolve(axis=Axis((1295, 10.35, -1535), (0, -1, 0)), mode=Mode.SUBTRACT)

    # 阵列(圆周)2 copy 19 sketch → 阵列(圆周)2 copy 19 (revolve, cut)
    with BuildSketch(Plane(origin=(1295, 4, -1615), x_dir=(0, 0, -1), z_dir=(-1, 0, 0))):
        Polygon((0, 0), (0, 1269.004303095), (5, 1266), (5, 0), align=None)
    revolve(axis=Axis((1295, 10.35, -1615), (0, -1, 0)), mode=Mode.SUBTRACT)

    # 阵列(圆周)2 copy 20 sketch → 阵列(圆周)2 copy 20 (revolve, cut)
    with BuildSketch(Plane(origin=(1295, 4, -1695), x_dir=(0, 0, -1), z_dir=(-1, 0, 0))):
        Polygon((0, 0), (0, 1269.004303095), (5, 1266), (5, 0), align=None)
    revolve(axis=Axis((1295, 10.35, -1695), (0, -1, 0)), mode=Mode.SUBTRACT)

    # 阵列(圆周)2 copy 21 sketch → 阵列(圆周)2 copy 21 (revolve, cut)
    with BuildSketch(Plane(origin=(1295, 4, -1775), x_dir=(0, 0, -1), z_dir=(-1, 0, 0))):
        Polygon((0, 0), (0, 1269.004303095), (5, 1266), (5, 0), align=None)
    revolve(axis=Axis((1295, 10.35, -1775), (0, -1, 0)), mode=Mode.SUBTRACT)

    # 阵列(圆周)2 copy 22 sketch → 阵列(圆周)2 copy 22 (revolve, cut)
    with BuildSketch(Plane(origin=(1295, 4, -1855), x_dir=(0, 0, -1), z_dir=(-1, 0, 0))):
        Polygon((0, 0), (0, 1269.004303095), (5, 1266), (5, 0), align=None)
    revolve(axis=Axis((1295, 10.35, -1855), (0, -1, 0)), mode=Mode.SUBTRACT)

    # 阵列(圆周)2 copy 23 sketch → 阵列(圆周)2 copy 23 (revolve, cut)
    with BuildSketch(Plane(origin=(1295, 4, -1935), x_dir=(0, 0, -1), z_dir=(-1, 0, 0))):
        Polygon((0, 0), (0, 1269.004303095), (5, 1266), (5, 0), align=None)
    revolve(axis=Axis((1295, 10.35, -1935), (0, -1, 0)), mode=Mode.SUBTRACT)

    # 阵列(圆周)2 copy 24 sketch → 阵列(圆周)2 copy 24 (revolve, cut)
    with BuildSketch(Plane(origin=(1295, 4, -2015), x_dir=(0, 0, -1), z_dir=(-1, 0, 0))):
        Polygon((0, 0), (0, 1269.004303095), (5, 1266), (5, 0), align=None)
    revolve(axis=Axis((1295, 10.35, -2015), (0, -1, 0)), mode=Mode.SUBTRACT)

    # 阵列(圆周)2 copy 25 sketch → 阵列(圆周)2 copy 25 (revolve, cut)
    with BuildSketch(Plane(origin=(1295, 4, -2095), x_dir=(0, 0, -1), z_dir=(-1, 0, 0))):
        Polygon((0, 0), (0, 1269.004303095), (5, 1266), (5, 0), align=None)
    revolve(axis=Axis((1295, 10.35, -2095), (0, -1, 0)), mode=Mode.SUBTRACT)

    # 阵列(圆周)2 copy 26 sketch → 阵列(圆周)2 copy 26 (revolve, cut)
    with BuildSketch(Plane(origin=(1295, 4, -2175), x_dir=(0, 0, -1), z_dir=(-1, 0, 0))):
        Polygon((0, 0), (0, 1269.004303095), (5, 1266), (5, 0), align=None)
    revolve(axis=Axis((1295, 10.35, -2175), (0, -1, 0)), mode=Mode.SUBTRACT)

    # 阵列(圆周)2 copy 27 sketch → 阵列(圆周)2 copy 27 (revolve, cut)
    with BuildSketch(Plane(origin=(1295, 4, -2255), x_dir=(0, 0, -1), z_dir=(-1, 0, 0))):
        Polygon((0, 0), (0, 1269.004303095), (5, 1266), (5, 0), align=None)
    revolve(axis=Axis((1295, 10.35, -2255), (0, -1, 0)), mode=Mode.SUBTRACT)

    # 阵列(圆周)2 copy 28 sketch → 阵列(圆周)2 copy 28 (revolve, cut)
    with BuildSketch(Plane(origin=(1295, 4, -2335), x_dir=(0, 0, -1), z_dir=(-1, 0, 0))):
        Polygon((0, 0), (0, 1269.004303095), (5, 1266), (5, 0), align=None)
    revolve(axis=Axis((1295, 10.35, -2335), (0, -1, 0)), mode=Mode.SUBTRACT)

    # 阵列(圆周)2 copy 29 sketch → 阵列(圆周)2 copy 29 (revolve, cut)
    with BuildSketch(Plane(origin=(1295, 4, -2415), x_dir=(0, 0, -1), z_dir=(-1, 0, 0))):
        Polygon((0, 0), (0, 1269.004303095), (5, 1266), (5, 0), align=None)
    revolve(axis=Axis((1295, 10.35, -2415), (0, -1, 0)), mode=Mode.SUBTRACT)


solid = part.part
